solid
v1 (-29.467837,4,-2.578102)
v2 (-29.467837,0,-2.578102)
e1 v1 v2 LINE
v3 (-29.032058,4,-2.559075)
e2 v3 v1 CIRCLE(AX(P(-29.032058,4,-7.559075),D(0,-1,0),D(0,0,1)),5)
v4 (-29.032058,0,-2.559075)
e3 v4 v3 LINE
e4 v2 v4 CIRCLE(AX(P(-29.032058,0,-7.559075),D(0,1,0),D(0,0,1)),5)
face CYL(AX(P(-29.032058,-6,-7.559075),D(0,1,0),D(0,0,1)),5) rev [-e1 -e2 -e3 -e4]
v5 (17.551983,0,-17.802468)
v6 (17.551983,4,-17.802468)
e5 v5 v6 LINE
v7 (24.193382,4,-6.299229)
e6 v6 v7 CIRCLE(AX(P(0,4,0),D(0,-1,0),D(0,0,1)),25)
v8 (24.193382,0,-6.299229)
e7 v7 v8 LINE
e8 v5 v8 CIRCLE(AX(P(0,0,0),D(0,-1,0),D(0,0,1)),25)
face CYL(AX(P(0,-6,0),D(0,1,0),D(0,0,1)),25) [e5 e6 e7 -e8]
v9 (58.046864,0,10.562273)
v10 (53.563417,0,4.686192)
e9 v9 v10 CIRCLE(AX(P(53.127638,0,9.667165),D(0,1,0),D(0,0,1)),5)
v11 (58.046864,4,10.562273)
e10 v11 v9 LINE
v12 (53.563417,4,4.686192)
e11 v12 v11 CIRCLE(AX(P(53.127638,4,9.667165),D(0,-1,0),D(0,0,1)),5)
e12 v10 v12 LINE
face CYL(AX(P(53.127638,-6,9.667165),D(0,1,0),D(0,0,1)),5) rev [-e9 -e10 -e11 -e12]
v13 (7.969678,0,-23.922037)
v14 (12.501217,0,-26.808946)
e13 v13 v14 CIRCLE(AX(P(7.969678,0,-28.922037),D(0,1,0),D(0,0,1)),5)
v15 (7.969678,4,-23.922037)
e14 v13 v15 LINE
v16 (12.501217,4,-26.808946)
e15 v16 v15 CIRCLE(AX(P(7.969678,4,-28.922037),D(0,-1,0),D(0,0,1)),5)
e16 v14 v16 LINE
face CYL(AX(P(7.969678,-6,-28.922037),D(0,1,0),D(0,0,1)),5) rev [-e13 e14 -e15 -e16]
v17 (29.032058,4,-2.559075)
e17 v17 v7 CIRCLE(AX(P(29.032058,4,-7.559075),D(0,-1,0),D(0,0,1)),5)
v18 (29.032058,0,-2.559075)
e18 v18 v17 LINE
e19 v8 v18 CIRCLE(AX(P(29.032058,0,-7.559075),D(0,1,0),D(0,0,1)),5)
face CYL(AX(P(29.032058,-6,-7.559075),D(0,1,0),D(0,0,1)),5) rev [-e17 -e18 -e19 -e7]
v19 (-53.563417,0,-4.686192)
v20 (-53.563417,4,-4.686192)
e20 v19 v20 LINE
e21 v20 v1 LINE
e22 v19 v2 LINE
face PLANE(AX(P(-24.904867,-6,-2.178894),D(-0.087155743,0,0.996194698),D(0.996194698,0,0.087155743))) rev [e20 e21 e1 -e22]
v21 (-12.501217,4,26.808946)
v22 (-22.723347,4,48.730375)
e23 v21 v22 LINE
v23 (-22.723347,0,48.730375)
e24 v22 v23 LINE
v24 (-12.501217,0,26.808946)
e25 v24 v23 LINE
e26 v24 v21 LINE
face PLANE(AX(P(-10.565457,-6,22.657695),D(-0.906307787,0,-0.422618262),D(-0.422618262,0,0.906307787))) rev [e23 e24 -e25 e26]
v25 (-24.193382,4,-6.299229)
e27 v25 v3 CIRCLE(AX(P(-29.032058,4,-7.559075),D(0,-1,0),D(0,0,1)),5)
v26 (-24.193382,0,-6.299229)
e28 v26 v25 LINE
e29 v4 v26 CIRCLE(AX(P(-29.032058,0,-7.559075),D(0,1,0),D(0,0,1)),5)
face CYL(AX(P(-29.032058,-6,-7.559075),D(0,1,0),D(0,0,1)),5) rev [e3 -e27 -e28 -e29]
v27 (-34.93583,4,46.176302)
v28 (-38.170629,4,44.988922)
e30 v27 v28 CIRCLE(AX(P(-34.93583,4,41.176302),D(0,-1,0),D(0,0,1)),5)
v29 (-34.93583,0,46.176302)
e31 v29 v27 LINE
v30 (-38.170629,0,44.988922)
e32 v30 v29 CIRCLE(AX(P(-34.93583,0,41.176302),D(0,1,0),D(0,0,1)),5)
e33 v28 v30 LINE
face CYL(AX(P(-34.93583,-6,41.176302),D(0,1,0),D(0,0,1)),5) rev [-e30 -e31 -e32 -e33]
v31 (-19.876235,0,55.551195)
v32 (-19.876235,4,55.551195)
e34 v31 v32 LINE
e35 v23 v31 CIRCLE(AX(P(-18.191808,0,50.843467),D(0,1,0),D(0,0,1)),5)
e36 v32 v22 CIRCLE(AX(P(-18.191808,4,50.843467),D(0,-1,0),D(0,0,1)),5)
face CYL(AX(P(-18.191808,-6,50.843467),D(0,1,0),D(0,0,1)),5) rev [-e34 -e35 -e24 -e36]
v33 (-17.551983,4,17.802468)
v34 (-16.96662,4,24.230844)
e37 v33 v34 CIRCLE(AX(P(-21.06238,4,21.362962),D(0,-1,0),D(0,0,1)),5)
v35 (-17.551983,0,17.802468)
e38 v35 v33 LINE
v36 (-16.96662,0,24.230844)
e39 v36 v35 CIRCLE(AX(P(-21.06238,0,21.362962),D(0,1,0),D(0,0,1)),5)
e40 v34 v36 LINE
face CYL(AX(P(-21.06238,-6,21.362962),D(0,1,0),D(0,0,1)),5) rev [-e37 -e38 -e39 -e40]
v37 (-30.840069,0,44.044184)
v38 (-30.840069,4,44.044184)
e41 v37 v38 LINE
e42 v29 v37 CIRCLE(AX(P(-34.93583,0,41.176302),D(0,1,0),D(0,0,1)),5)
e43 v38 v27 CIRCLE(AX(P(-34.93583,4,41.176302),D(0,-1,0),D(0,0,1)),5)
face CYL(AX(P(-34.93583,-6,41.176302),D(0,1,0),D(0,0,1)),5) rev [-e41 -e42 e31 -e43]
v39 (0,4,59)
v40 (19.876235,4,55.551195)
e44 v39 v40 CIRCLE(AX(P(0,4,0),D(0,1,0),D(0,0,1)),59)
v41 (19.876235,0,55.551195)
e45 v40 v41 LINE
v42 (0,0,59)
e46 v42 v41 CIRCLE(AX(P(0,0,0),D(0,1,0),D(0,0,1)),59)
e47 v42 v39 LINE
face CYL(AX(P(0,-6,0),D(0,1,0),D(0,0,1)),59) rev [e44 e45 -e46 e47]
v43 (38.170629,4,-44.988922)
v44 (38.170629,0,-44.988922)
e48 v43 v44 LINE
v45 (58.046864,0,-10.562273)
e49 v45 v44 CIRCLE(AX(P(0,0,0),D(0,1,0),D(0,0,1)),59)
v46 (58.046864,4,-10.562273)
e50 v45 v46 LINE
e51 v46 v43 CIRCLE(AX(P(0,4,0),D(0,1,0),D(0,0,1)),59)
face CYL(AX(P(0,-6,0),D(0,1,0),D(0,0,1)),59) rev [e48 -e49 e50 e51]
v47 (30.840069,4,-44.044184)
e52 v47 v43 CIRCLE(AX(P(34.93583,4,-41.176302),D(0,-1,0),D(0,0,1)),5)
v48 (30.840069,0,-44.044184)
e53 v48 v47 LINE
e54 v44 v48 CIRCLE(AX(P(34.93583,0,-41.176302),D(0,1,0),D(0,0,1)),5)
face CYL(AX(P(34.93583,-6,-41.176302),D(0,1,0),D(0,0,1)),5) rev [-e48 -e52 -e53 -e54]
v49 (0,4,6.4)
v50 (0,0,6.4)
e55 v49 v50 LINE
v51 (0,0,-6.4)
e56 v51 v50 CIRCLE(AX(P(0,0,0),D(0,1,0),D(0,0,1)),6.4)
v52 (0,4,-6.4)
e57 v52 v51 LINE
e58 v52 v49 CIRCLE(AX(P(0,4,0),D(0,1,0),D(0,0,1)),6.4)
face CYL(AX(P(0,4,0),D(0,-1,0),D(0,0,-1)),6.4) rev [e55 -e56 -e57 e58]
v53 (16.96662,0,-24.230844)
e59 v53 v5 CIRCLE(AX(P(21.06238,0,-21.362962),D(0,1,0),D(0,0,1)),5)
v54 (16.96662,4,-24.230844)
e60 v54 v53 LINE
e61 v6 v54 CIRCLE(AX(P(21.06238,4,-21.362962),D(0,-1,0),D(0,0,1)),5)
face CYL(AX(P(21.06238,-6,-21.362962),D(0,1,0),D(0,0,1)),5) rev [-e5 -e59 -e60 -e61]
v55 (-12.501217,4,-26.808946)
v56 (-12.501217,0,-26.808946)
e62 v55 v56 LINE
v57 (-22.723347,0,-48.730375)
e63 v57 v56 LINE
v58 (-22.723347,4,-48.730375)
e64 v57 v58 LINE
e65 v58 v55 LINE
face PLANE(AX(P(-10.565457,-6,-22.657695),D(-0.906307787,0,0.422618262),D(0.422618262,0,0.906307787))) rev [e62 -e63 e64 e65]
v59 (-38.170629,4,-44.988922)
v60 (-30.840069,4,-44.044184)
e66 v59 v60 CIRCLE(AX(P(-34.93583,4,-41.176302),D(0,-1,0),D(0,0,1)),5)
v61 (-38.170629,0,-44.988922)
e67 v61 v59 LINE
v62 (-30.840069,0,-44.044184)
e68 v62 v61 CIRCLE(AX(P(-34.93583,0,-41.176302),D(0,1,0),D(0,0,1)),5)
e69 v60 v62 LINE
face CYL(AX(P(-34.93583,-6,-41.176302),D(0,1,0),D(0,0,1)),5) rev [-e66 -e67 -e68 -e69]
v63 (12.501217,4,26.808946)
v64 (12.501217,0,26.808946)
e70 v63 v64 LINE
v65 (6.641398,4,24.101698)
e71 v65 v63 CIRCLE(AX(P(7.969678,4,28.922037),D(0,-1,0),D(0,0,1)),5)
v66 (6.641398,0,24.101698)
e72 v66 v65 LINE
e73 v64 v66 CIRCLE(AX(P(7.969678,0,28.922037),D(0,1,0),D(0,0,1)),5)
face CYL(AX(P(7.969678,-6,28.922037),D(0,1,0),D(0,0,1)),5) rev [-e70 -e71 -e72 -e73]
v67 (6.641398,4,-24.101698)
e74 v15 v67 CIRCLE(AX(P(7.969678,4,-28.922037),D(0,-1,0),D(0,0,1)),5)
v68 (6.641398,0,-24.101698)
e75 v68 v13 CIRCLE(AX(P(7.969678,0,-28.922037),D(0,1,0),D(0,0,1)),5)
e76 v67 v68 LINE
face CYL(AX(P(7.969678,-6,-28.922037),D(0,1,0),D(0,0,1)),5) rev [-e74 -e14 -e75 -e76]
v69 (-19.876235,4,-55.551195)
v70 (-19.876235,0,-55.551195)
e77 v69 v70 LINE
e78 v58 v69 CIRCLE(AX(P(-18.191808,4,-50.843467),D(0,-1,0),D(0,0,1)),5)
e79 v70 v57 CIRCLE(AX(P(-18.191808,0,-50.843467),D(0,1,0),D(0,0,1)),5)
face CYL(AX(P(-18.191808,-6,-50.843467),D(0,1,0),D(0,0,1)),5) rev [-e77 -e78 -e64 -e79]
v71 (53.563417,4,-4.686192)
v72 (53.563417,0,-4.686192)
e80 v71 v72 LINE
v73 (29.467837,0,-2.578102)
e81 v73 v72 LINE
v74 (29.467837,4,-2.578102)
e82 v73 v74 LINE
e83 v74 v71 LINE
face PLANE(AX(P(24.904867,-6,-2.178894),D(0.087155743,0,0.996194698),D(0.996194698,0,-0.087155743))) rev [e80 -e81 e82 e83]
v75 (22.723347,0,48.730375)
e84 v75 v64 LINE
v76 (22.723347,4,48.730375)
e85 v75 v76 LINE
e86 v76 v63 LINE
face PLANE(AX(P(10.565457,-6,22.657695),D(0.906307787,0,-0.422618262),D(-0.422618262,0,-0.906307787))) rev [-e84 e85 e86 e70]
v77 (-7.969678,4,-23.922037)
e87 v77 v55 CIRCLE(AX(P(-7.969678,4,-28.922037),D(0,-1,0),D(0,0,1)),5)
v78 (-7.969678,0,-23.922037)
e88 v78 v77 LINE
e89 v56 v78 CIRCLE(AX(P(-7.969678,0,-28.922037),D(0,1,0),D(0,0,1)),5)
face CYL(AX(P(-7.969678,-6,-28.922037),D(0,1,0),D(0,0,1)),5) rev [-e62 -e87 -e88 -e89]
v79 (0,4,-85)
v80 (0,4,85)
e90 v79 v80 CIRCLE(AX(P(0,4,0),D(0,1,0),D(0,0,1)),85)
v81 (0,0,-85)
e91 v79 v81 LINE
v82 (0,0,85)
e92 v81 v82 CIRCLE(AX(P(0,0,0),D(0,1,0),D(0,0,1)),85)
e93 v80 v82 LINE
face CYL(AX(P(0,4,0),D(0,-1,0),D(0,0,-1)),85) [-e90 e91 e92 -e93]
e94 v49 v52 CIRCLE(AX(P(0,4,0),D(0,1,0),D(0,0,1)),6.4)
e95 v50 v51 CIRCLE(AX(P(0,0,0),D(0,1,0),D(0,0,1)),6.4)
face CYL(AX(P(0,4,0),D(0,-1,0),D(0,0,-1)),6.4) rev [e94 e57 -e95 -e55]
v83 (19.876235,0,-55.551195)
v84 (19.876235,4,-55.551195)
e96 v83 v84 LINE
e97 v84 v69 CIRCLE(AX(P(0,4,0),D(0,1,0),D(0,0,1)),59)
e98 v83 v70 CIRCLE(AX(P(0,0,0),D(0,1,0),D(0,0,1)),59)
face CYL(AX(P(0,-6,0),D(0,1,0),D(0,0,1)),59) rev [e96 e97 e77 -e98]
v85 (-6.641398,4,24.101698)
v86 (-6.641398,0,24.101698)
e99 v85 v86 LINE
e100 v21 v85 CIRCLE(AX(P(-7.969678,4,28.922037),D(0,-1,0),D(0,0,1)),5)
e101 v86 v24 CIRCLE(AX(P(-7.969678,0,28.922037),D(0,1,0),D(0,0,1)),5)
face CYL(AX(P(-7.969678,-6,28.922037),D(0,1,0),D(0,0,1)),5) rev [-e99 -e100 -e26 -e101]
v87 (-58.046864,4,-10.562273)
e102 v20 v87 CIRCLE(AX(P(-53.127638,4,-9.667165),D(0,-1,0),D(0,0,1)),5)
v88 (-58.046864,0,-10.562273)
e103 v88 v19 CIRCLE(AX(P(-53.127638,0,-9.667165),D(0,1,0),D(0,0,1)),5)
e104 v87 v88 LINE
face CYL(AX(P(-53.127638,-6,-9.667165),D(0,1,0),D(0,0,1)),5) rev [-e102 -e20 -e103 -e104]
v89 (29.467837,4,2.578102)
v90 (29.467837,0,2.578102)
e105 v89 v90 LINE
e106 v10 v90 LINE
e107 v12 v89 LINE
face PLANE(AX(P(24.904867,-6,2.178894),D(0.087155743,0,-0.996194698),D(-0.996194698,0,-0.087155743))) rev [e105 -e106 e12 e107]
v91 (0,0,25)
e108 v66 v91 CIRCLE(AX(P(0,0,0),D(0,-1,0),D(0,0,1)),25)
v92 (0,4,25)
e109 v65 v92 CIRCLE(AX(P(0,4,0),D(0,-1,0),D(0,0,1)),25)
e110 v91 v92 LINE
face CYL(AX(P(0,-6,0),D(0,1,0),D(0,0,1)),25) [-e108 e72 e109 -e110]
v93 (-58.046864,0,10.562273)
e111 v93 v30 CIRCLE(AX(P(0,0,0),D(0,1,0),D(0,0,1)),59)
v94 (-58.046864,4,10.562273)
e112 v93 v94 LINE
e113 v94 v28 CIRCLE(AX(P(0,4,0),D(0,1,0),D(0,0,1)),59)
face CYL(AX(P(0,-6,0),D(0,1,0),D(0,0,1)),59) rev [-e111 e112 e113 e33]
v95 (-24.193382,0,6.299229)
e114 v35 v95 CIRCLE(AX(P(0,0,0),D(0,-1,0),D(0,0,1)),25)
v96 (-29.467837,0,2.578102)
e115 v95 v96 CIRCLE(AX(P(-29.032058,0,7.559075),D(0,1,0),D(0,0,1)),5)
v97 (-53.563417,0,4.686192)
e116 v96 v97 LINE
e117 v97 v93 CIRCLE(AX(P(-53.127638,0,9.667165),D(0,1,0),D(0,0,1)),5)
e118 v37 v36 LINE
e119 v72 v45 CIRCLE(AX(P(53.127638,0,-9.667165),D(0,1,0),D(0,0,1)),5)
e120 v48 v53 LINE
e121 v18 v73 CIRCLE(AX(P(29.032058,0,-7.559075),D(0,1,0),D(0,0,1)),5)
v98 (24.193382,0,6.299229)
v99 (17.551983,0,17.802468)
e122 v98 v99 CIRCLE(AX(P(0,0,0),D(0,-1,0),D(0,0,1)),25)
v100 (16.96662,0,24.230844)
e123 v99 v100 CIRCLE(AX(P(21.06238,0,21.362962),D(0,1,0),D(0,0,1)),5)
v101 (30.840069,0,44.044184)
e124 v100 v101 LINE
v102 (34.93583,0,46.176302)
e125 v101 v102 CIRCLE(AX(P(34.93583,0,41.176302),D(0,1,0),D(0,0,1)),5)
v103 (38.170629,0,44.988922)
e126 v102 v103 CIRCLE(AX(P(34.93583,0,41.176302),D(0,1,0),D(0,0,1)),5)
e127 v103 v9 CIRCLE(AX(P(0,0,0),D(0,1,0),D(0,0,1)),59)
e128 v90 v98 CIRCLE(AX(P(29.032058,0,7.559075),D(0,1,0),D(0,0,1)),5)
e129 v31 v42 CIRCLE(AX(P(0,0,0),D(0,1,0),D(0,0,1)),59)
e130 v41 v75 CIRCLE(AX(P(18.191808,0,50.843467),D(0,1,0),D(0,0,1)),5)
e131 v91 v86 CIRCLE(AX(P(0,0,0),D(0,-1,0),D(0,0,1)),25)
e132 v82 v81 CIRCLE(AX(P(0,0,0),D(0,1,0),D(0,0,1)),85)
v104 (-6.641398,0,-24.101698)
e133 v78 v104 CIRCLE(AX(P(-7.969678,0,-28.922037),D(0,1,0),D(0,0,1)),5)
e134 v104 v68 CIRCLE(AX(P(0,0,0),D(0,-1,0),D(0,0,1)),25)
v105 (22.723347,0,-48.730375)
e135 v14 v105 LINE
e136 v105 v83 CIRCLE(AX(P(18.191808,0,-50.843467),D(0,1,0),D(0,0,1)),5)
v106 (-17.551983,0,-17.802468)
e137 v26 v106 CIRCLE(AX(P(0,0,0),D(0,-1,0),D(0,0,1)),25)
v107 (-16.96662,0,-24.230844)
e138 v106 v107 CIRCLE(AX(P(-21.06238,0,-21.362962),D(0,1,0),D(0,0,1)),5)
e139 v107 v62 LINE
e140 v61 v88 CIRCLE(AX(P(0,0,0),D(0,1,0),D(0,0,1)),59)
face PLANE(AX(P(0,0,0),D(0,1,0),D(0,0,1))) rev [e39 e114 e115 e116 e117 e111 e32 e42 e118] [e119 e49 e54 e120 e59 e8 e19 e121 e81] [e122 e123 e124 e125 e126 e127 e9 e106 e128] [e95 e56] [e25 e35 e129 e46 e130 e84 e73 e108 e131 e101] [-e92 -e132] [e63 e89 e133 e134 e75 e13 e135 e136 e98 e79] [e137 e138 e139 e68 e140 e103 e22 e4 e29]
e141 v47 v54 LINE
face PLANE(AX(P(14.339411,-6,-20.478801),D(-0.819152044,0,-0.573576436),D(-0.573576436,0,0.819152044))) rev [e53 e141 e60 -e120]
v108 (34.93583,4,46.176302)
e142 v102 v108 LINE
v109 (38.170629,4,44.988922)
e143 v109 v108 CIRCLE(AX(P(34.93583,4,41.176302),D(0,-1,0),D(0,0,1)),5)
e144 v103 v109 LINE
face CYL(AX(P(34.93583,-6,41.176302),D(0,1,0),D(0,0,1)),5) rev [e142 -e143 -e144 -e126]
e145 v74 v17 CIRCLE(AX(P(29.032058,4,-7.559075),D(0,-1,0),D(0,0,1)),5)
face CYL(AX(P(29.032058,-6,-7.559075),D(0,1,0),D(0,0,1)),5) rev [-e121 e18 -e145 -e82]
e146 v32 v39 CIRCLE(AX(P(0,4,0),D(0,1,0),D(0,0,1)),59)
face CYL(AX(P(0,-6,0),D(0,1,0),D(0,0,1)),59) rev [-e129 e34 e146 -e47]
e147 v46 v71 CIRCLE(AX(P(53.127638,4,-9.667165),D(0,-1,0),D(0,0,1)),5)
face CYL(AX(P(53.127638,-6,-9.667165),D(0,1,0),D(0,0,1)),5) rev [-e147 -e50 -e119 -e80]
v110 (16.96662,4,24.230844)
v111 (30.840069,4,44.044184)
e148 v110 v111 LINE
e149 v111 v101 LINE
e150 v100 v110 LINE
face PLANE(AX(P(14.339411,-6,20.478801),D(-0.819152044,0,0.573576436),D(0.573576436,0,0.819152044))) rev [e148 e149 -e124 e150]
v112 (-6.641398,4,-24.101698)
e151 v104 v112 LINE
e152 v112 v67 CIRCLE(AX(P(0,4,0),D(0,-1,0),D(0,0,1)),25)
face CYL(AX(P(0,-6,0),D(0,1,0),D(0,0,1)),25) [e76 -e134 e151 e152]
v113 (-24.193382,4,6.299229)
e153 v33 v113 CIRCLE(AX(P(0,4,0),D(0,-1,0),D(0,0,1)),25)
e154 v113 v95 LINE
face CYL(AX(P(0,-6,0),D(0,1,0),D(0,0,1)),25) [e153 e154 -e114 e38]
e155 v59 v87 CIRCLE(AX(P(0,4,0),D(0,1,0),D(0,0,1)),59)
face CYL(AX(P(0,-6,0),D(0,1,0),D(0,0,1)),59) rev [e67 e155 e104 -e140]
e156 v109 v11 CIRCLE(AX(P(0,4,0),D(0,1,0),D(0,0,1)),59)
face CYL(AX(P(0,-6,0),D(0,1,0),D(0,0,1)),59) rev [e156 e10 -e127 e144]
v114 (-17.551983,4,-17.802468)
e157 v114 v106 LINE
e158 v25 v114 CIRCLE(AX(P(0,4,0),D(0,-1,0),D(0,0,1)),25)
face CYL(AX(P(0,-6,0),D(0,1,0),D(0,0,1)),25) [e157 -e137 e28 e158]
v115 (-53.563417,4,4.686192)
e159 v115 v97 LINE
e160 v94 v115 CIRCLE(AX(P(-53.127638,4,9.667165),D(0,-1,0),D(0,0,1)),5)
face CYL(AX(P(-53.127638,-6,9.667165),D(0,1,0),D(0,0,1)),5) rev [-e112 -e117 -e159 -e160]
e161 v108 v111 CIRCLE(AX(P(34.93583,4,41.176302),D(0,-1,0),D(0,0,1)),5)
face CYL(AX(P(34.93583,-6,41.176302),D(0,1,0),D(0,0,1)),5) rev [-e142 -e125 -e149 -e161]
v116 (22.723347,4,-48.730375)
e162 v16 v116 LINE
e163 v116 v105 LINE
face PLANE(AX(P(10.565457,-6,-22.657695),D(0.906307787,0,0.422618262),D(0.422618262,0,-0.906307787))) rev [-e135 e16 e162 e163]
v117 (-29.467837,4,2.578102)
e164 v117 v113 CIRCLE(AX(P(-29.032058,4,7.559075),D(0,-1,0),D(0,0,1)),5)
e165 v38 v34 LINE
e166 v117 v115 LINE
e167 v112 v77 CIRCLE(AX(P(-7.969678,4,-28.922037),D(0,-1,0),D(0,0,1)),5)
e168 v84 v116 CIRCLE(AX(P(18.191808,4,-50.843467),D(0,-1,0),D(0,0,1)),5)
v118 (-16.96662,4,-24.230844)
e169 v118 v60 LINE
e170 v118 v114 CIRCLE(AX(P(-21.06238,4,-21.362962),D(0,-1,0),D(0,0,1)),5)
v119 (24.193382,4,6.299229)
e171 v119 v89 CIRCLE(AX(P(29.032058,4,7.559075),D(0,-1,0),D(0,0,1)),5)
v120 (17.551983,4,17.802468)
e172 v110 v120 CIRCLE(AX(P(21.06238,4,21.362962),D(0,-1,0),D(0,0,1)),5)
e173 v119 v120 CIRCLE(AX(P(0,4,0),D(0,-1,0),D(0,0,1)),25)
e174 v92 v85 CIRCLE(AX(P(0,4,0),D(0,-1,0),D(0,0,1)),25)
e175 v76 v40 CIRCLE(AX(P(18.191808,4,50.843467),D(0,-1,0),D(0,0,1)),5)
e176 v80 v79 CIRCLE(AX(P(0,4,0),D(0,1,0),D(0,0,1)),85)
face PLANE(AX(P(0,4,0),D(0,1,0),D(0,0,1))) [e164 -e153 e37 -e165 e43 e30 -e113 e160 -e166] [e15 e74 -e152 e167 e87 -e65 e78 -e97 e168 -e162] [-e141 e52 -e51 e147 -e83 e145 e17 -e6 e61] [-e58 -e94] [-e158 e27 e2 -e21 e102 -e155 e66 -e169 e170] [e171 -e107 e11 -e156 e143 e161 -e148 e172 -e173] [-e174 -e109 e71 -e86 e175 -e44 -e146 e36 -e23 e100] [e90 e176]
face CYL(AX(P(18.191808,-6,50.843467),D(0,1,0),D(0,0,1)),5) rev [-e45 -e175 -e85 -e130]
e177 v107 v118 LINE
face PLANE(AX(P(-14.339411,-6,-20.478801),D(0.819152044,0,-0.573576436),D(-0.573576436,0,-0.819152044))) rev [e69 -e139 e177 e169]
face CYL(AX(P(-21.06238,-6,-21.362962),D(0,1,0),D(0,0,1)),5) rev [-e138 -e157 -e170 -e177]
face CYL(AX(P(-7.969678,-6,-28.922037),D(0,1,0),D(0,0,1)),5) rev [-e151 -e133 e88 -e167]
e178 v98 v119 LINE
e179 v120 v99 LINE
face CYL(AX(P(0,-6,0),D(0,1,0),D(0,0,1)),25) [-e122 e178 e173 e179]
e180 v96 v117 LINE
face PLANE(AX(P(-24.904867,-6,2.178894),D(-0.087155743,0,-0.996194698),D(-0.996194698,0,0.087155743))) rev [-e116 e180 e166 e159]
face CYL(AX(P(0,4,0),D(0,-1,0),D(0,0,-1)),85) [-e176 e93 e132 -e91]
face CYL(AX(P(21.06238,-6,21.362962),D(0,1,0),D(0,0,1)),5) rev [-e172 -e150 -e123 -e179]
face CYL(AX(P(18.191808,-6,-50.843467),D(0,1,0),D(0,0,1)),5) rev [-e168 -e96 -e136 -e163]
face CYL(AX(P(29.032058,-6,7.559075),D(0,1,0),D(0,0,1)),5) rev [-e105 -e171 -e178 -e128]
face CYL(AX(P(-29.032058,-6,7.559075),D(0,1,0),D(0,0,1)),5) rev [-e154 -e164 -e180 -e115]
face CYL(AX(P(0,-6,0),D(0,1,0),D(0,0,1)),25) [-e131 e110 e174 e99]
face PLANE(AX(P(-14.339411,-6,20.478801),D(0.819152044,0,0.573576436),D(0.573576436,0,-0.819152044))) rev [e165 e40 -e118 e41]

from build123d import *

# Parameters (mm, degrees)
SKETCH1_R           = 85
SKETCH1_R_2         = 6.4
BOSS_EXTRUDE1_DEPTH = 4
CUT_EXTRUDE1_DEPTH  = 10
FILLET1_R           = 5


with BuildPart() as part:
    # Sketch1 → Boss-Extrude1 (new body)
    with BuildSketch(Plane(origin=(0, 0, 0), x_dir=(1, 0, 0), z_dir=(0, 1, 0))):
        with Locations(Location((0, 0, 0), (0, 0, 270))):
            Circle(SKETCH1_R)
        with Locations(Location((0, 0, 0), (0, 0, 270))):
            Circle(SKETCH1_R_2, mode=Mode.SUBTRACT)
    extrude(amount=BOSS_EXTRUDE1_DEPTH)

    # Sketch2 → Cut-Extrude1 (cut)
    with BuildSketch(Plane(origin=(0, 4, 0), x_dir=(1, 0, 0), z_dir=(0, 1, 0))):
        with BuildLine():
            Line((10.565456544, 22.657694676), (24.934477443, 53.472159435))
            ThreePointArc((24.934477443, 53.472159435), (0, 59), (-24.934477443, 53.472159435))
            Line((-24.934477443, 53.472159435), (-10.565456544, 22.657694676))
            ThreePointArc((-10.565456544, 22.657694676), (0, 25), (10.565456544, 22.657694676))
        make_face()
        with BuildLine():
            Line((14.339410909, 20.478801107), (33.841009745, 48.329970613))
            ThreePointArc((33.841009745, 48.329970613), (51.095498823, 29.5), (58.775487187, 5.142188822))
            Line((58.775487187, 5.142188822), (24.904867452, 2.178893569))
            ThreePointArc((24.904867452, 2.178893569), (21.650635095, 12.5), (14.339410909, 20.478801107))
        make_face()
        with BuildLine():
            Line((24.904867452, -2.178893569), (58.775487187, -5.142188822))
            ThreePointArc((58.775487187, -5.142188822), (51.095498823, -29.5), (33.841009745, -48.329970613))
            Line((33.841009745, -48.329970613), (14.339410909, -20.478801107))
            ThreePointArc((14.339410909, -20.478801107), (21.650635095, -12.5), (24.904867452, -2.178893569))
        make_face()
        with BuildLine():
            Line((10.565456544, -22.657694676), (24.934477443, -53.472159435))
            ThreePointArc((24.934477443, -53.472159435), (0, -59), (-24.934477443, -53.472159435))
            Line((-24.934477443, -53.472159435), (-10.565456544, -22.657694676))
            ThreePointArc((-10.565456544, -22.657694676), (0, -25), (10.565456544, -22.657694676))
        make_face()
        with BuildLine():
            Line((-14.339410909, -20.478801107), (-33.841009745, -48.329970613))
            ThreePointArc((-33.841009745, -48.329970613), (-51.095498823, -29.5), (-58.775487187, -5.142188822))
            Line((-58.775487187, -5.142188822), (-24.904867452, -2.178893569))
            ThreePointArc((-24.904867452, -2.178893569), (-21.650635095, -12.5), (-14.339410909, -20.478801107))
        make_face()
        with BuildLine():
            Line((-24.904867452, 2.178893569), (-58.775487187, 5.142188822))
            ThreePointArc((-58.775487187, 5.142188822), (-51.095498823, 29.5), (-33.841009745, 48.329970613))
            Line((-33.841009745, 48.329970613), (-14.339410909, 20.478801107))
            ThreePointArc((-14.339410909, 20.478801107), (-21.650635095, 12.5), (-24.904867452, 2.178893569))
        make_face()
    extrude(amount=-CUT_EXTRUDE1_DEPTH, mode=Mode.SUBTRACT)

    # Fillet1
    fillet1_edges = [part.edges().sort_by_distance(p)[0] for p in [
        (-10.565456544, 2, 22.657694676),
        (10.565456544, 2, 22.657694676),
        (24.934477443, 2, 53.472159435),
        (-24.934477443, 2, 53.472159435),
        (-24.904867452, 2, 2.178893569),
        (-14.339410909, 2, 20.478801107),
        (-33.841009745, 2, 48.329970613),
        (-58.775487187, 2, 5.142188822),
        (14.339410909, 2, 20.478801107),
        (24.904867452, 2, 2.178893569),
        (58.775487187, 2, 5.142188822),
        (33.841009745, 2, 48.329970613),
        (24.904867452, 2, -2.178893569),
        (14.339410909, 2, -20.478801107),
        (33.841009745, 2, -48.329970613),
        (58.775487187, 2, -5.142188822),
        (-14.339410909, 2, -20.478801107),
        (-24.904867452, 2, -2.178893569),
        (-58.775487187, 2, -5.142188822),
        (-33.841009745, 2, -48.329970613),
        (10.565456544, 2, -22.657694676),
        (-10.565456544, 2, -22.657694676),
        (-24.934477443, 2, -53.472159435),
        (24.934477443, 2, -53.472159435),
    ]]
    fillet(fillet1_edges, radius=FILLET1_R)


solid = part.part
